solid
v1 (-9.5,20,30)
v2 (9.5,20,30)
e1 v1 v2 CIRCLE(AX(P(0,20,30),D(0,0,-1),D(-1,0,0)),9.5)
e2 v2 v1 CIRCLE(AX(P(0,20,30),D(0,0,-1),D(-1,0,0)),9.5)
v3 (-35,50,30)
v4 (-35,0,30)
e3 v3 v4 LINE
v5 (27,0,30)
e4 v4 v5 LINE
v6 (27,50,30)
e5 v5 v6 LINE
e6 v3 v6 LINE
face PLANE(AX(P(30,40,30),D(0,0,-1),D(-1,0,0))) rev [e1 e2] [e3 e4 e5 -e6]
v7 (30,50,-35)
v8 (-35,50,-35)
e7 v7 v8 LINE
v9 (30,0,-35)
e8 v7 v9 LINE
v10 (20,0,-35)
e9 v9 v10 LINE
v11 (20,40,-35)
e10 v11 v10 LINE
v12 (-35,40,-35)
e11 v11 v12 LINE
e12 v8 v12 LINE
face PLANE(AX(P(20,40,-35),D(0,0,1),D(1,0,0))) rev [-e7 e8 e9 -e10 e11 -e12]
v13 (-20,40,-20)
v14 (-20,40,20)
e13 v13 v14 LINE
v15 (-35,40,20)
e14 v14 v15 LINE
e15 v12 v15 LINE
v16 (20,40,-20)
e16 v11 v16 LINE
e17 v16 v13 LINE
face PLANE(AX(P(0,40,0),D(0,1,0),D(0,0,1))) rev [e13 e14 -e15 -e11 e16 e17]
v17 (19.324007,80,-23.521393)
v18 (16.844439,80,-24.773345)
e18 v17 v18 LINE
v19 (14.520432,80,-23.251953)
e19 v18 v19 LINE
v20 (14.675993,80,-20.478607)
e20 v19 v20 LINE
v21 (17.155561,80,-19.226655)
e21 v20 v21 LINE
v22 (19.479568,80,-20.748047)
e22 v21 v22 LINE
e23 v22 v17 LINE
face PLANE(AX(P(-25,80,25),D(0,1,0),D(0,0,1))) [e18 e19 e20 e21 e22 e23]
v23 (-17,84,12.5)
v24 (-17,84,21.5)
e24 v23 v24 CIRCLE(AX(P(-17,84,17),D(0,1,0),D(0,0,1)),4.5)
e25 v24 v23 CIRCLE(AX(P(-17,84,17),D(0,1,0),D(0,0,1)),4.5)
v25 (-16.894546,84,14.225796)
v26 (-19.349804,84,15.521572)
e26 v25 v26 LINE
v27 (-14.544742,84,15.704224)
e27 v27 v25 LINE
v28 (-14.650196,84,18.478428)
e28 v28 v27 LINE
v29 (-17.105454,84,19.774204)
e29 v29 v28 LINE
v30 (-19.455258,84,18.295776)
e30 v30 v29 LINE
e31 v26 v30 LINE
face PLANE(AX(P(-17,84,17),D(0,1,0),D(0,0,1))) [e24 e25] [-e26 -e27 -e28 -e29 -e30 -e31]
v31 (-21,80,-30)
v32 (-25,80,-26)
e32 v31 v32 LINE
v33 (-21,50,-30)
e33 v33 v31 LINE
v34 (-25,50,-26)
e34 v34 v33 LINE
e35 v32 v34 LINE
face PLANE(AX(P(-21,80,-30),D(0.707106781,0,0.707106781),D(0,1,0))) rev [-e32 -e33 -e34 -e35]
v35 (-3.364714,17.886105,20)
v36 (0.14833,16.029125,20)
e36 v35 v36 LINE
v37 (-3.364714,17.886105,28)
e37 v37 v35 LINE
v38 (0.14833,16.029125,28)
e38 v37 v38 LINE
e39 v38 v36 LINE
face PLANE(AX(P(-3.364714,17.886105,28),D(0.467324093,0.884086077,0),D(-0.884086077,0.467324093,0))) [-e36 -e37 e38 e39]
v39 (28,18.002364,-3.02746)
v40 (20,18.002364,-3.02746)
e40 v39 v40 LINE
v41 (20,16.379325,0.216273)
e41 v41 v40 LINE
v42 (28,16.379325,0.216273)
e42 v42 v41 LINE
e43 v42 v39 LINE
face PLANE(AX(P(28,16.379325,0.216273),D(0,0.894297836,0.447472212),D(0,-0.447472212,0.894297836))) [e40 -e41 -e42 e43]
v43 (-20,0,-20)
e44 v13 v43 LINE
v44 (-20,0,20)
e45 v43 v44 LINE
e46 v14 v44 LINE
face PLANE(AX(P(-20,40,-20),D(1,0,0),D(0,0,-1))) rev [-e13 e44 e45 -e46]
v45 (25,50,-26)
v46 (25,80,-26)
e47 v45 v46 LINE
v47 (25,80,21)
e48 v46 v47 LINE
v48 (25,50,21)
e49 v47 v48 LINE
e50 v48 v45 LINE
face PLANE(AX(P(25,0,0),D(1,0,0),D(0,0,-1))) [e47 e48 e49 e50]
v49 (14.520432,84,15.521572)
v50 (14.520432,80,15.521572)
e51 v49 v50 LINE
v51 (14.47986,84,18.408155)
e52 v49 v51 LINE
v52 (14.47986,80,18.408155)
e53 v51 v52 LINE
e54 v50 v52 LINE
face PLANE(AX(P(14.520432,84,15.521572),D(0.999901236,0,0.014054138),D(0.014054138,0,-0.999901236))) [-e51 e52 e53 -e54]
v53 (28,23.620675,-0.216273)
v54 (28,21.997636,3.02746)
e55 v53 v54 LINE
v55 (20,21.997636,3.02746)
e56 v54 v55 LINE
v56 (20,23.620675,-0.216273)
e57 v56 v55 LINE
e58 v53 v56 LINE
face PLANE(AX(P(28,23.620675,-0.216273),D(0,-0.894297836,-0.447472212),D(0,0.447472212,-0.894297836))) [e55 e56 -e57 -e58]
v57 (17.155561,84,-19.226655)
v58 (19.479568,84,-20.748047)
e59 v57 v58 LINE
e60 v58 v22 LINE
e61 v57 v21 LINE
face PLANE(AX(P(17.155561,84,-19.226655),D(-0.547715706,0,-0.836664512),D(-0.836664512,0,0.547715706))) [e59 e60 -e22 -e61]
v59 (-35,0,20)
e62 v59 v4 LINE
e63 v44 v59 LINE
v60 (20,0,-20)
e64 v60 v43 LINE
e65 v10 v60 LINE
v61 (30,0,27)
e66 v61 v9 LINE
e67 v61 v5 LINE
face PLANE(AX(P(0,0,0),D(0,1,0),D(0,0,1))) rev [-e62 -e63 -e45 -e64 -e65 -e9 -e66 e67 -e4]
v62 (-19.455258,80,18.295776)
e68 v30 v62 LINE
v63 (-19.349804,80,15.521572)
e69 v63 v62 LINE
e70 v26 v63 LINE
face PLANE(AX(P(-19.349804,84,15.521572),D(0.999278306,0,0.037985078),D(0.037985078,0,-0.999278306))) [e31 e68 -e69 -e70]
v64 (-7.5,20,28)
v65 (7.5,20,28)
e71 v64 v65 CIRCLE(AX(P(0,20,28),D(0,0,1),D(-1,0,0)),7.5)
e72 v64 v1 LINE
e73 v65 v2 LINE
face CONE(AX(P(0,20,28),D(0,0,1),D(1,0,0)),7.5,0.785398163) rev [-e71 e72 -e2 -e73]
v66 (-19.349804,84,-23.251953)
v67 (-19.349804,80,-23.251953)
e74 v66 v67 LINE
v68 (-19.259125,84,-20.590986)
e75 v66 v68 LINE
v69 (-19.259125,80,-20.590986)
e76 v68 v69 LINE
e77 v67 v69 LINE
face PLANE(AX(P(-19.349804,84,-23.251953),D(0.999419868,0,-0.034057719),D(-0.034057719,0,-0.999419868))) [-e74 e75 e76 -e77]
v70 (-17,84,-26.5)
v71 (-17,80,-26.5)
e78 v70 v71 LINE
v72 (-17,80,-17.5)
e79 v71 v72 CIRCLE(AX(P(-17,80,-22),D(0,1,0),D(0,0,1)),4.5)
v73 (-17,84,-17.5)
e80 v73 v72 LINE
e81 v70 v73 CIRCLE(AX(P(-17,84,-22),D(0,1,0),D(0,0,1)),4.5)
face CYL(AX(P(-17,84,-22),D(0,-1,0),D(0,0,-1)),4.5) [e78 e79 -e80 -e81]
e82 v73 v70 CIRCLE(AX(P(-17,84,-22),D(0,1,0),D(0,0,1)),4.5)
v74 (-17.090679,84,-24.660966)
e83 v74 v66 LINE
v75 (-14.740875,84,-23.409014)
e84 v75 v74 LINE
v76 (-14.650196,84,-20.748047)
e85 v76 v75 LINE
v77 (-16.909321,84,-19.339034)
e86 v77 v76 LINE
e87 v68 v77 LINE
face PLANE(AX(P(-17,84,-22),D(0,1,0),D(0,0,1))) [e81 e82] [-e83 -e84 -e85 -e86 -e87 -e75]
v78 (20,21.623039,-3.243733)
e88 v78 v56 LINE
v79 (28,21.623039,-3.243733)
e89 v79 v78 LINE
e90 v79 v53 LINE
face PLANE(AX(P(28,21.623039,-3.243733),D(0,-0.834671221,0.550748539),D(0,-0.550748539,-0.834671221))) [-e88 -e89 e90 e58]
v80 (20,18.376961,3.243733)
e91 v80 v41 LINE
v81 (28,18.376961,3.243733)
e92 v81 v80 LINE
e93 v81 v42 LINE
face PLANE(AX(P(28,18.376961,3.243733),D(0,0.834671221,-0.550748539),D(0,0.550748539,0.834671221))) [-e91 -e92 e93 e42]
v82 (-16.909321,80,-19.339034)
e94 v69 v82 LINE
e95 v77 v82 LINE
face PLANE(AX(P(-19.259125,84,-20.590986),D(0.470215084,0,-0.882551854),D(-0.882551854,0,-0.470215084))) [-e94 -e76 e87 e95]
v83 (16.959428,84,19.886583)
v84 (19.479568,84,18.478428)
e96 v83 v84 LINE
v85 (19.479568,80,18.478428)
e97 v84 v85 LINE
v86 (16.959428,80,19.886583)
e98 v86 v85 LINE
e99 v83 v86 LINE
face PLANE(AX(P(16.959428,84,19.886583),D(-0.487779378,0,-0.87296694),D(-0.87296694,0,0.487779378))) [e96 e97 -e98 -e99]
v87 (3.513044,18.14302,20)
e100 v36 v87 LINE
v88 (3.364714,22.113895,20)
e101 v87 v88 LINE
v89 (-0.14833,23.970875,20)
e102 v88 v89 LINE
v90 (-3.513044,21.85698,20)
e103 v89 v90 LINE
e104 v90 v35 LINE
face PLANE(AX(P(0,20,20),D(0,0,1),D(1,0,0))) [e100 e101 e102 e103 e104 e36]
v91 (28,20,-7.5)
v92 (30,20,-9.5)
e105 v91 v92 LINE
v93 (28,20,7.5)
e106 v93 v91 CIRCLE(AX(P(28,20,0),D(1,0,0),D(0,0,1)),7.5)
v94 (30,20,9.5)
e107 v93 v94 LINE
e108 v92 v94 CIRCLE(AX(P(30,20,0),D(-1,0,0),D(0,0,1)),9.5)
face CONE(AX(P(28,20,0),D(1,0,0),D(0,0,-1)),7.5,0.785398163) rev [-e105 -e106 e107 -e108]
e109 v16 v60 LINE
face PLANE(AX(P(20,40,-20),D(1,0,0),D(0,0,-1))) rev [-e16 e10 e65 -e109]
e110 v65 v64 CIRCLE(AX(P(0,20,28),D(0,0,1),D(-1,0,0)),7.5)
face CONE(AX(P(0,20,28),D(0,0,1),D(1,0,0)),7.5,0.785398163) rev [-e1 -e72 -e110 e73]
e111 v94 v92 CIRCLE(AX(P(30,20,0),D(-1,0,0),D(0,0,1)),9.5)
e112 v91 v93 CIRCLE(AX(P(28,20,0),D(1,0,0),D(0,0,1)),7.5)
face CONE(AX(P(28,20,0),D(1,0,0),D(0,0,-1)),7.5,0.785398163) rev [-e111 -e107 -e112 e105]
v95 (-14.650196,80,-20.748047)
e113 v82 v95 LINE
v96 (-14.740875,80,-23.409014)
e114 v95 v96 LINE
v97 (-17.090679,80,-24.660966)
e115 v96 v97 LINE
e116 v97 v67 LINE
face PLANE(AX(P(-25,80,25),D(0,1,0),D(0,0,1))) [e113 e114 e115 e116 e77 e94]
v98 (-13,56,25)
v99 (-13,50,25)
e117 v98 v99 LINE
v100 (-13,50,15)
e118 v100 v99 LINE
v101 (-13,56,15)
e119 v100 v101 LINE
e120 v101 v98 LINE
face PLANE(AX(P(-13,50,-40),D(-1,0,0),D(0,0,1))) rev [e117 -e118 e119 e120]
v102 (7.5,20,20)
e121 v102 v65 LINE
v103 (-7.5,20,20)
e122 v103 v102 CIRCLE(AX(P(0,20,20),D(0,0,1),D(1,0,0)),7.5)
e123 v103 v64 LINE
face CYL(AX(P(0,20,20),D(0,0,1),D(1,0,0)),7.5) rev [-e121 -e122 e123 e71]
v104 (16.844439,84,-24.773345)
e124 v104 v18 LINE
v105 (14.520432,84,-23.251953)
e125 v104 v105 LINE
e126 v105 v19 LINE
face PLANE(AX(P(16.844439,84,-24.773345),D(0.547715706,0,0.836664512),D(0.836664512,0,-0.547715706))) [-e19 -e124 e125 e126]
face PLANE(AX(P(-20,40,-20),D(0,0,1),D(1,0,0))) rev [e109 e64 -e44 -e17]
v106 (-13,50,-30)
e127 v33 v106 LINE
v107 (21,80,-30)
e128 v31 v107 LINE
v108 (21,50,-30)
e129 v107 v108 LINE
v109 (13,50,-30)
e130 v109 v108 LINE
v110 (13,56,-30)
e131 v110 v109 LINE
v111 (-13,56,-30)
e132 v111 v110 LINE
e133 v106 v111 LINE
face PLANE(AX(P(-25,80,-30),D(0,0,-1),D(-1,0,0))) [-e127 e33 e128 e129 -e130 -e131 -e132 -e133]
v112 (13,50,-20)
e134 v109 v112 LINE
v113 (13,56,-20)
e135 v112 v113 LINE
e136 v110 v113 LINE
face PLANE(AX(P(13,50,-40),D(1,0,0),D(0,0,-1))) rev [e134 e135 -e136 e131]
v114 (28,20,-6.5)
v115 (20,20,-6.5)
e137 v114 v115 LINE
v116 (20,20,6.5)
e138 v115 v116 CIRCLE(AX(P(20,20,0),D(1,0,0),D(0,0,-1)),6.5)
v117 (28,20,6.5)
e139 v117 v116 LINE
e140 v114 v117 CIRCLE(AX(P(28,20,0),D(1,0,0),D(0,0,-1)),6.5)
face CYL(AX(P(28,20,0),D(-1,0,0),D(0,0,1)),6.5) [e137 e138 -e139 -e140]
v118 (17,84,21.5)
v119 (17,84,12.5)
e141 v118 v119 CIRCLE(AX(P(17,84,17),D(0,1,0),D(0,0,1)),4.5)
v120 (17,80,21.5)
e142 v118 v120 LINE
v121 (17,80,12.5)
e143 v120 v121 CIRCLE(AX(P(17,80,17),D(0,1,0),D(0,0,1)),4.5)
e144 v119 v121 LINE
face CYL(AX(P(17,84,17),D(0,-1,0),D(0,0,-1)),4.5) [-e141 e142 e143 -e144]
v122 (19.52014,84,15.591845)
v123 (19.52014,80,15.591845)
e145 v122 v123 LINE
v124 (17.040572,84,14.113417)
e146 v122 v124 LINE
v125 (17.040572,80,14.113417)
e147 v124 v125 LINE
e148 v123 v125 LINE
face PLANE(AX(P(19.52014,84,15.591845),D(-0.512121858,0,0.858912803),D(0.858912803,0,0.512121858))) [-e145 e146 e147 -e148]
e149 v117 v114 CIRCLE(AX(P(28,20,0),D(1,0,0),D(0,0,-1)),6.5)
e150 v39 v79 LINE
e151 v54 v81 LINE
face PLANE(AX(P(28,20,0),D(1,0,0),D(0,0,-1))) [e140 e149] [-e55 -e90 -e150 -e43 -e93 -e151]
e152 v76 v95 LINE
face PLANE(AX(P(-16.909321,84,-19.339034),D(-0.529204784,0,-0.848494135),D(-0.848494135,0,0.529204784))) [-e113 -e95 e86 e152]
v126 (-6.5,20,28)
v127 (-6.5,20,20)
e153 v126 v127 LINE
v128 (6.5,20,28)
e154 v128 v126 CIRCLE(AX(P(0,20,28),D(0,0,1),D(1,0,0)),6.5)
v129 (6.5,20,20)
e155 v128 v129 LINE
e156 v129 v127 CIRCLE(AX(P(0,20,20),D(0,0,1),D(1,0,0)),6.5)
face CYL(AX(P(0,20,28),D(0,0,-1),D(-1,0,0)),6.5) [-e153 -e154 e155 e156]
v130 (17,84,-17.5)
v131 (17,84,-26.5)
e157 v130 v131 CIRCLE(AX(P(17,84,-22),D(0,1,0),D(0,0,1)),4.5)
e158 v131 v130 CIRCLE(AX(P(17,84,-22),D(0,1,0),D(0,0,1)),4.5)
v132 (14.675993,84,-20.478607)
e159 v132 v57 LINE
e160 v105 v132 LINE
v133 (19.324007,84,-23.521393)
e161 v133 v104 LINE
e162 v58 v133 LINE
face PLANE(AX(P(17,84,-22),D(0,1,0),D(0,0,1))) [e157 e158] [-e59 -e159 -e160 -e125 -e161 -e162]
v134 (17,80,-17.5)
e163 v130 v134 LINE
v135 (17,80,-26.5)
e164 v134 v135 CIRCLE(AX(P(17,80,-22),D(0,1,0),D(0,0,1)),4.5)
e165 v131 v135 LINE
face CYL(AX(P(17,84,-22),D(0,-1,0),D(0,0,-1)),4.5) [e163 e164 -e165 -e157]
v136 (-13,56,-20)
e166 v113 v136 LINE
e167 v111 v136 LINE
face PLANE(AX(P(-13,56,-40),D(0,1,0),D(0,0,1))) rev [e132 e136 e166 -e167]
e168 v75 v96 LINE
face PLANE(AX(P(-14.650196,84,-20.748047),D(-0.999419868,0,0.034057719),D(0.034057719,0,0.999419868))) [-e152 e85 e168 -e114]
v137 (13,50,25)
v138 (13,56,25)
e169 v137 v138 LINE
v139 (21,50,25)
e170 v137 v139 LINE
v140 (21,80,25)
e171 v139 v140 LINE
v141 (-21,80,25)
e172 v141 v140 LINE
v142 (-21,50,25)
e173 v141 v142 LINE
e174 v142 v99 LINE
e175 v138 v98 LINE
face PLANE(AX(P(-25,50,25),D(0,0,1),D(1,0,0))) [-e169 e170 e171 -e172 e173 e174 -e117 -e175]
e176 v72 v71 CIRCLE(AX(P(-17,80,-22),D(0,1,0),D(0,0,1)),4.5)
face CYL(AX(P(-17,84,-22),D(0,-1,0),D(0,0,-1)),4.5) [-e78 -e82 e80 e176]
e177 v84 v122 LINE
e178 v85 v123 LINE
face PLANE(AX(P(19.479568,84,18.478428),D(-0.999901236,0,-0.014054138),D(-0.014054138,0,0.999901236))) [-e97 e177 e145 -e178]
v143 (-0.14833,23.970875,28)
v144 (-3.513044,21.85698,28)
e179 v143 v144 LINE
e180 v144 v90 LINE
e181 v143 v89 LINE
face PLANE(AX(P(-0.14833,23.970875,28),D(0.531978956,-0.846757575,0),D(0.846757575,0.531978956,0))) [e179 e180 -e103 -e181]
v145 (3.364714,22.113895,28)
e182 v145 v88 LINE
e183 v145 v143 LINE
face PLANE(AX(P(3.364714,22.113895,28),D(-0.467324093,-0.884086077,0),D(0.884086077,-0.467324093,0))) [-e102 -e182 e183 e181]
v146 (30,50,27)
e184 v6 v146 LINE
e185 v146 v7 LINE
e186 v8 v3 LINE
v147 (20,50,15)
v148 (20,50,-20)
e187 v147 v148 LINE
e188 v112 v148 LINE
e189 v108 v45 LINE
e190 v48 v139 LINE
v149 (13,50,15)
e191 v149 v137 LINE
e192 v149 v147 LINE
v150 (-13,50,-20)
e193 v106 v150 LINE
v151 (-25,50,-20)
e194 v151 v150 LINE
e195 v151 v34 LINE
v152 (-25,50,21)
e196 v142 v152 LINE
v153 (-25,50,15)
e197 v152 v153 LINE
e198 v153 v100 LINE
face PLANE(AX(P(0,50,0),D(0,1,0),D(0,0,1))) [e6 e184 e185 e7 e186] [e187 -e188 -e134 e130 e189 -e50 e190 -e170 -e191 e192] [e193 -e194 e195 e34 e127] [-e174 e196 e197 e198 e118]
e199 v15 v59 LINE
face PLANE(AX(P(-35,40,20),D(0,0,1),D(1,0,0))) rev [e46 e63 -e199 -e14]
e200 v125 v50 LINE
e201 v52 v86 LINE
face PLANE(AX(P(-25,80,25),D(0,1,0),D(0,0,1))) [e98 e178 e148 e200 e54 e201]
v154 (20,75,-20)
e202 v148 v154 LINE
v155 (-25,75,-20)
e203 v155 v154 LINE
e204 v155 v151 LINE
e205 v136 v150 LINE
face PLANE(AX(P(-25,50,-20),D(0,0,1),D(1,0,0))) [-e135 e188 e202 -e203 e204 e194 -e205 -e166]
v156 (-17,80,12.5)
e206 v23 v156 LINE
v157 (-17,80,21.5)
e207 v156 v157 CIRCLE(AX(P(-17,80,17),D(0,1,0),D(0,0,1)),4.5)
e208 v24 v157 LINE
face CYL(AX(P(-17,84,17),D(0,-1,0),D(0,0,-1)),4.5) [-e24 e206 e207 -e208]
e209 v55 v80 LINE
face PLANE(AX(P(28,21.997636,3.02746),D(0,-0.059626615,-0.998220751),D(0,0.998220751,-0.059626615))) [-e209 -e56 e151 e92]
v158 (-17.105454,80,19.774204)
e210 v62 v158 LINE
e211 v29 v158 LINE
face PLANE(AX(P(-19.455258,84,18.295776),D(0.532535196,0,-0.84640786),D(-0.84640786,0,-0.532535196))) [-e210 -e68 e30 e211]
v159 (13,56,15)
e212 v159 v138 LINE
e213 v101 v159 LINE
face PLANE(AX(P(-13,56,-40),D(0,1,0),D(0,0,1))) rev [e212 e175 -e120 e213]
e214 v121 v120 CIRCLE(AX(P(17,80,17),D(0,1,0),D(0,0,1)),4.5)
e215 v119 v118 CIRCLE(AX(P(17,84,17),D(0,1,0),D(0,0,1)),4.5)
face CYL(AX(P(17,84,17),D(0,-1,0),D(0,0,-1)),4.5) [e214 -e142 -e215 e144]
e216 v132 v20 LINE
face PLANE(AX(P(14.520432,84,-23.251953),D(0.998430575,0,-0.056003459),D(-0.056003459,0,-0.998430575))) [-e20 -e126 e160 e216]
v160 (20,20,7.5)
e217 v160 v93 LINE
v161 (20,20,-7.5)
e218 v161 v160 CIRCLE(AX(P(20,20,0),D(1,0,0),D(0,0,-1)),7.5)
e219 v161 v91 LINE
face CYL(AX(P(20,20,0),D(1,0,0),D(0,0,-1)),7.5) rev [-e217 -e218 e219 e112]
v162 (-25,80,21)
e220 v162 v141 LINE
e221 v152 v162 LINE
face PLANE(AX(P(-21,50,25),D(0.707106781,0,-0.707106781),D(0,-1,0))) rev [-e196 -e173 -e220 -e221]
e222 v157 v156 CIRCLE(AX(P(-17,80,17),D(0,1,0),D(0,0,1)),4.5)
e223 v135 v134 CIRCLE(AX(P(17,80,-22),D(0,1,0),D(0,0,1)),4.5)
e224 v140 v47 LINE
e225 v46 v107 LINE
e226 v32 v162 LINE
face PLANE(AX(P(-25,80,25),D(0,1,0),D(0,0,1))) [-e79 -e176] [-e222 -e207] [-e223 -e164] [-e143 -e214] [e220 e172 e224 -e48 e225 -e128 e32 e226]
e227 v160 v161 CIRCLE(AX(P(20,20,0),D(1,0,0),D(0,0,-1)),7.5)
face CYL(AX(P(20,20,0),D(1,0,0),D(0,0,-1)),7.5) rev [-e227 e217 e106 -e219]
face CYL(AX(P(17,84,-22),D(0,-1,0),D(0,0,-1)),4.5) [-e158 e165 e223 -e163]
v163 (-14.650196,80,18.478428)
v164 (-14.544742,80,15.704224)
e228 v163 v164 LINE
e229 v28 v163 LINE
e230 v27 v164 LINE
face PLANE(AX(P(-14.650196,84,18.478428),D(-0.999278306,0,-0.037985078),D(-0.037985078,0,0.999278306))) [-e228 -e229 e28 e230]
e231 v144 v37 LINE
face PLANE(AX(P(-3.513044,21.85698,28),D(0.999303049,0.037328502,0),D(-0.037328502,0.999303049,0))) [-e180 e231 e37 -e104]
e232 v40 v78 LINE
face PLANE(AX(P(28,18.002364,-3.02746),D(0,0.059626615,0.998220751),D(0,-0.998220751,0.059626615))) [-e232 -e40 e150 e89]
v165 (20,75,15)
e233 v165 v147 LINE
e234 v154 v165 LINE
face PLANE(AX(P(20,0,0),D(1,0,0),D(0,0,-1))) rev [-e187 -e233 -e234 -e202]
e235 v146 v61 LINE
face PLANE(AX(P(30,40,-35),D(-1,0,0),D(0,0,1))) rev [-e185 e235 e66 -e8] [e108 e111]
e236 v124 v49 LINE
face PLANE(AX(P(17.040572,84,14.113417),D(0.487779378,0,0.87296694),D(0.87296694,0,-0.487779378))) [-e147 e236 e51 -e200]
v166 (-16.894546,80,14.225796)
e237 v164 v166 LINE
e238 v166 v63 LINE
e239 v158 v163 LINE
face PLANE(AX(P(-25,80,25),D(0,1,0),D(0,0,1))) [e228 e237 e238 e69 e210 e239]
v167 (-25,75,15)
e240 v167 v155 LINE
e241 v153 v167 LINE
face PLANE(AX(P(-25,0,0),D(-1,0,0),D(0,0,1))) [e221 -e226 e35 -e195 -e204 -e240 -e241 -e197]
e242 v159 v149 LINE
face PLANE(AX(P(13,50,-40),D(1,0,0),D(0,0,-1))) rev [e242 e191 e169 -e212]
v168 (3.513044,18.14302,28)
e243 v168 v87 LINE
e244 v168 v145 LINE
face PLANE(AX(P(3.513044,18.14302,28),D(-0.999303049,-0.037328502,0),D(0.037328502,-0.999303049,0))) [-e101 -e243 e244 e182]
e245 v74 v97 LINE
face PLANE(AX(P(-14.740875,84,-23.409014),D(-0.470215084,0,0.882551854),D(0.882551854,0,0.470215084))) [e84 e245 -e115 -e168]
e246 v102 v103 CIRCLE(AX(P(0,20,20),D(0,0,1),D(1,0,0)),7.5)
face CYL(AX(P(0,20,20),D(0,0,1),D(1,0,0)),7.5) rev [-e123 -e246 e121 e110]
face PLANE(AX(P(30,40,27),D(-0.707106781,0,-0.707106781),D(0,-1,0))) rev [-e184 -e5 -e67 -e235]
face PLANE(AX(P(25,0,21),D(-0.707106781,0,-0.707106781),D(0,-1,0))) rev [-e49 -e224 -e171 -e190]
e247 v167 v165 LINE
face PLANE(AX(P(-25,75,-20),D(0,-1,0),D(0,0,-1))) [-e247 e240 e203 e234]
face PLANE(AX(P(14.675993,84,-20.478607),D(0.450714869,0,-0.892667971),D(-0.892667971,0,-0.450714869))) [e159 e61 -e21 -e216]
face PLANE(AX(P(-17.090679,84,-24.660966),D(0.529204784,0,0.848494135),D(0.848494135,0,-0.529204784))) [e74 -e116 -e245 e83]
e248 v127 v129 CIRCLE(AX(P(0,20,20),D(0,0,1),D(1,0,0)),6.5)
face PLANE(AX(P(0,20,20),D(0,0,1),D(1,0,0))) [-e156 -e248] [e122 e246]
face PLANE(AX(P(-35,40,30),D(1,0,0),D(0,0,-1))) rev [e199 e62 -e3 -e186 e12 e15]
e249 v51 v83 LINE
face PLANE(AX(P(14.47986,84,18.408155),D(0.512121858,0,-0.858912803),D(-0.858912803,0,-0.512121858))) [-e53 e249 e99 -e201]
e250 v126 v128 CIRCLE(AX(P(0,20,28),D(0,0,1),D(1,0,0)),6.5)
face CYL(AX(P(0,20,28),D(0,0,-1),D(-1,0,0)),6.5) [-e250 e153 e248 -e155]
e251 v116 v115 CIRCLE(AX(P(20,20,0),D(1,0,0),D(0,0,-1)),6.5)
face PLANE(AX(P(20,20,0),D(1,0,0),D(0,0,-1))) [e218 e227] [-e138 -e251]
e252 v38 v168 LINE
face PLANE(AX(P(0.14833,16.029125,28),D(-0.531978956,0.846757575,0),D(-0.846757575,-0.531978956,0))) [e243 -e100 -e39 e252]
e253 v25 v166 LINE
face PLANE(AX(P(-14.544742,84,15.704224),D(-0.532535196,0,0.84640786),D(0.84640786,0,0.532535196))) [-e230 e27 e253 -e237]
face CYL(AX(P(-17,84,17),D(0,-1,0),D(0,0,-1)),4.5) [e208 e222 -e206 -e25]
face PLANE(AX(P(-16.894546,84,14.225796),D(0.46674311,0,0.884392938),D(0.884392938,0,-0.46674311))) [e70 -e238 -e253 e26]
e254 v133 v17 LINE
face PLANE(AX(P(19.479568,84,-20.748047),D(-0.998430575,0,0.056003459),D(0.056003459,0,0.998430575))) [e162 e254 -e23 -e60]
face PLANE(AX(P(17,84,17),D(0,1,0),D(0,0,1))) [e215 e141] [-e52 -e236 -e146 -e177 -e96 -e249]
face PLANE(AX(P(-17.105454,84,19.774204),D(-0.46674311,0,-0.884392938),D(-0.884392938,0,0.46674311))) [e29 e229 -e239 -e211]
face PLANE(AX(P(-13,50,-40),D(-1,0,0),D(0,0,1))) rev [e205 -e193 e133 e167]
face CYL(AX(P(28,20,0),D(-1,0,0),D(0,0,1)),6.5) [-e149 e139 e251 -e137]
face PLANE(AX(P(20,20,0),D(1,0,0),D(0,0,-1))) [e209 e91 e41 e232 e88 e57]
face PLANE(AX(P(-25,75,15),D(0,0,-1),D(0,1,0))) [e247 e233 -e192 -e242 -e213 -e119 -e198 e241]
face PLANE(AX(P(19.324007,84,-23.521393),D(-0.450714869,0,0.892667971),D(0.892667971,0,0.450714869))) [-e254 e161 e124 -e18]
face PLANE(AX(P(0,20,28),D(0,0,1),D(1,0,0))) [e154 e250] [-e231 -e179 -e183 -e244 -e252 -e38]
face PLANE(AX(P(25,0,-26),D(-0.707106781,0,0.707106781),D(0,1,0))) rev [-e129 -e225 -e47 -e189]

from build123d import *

# Parameters (mm, degrees)
BOSS_EXTRUDE1_DEPTH  = 40
SKETCH3_W            = 65
SKETCH3_H            = 65
BOSS_EXTRUDE3_DEPTH  = 10
SKETCH4_R            = 7.5
CUT_EXTRUDE1_DEPTH   = 10
SKETCH5_R            = 7.5
CUT_EXTRUDE2_DEPTH   = 10
SKETCH6_R            = 6.5
BOSS_EXTRUDE4_DEPTH  = 8
SKETCH7_R            = 6.5
BOSS_EXTRUDE5_DEPTH  = 8
CHAMFER1_SIZE        = 2
CHAMFER2_SIZE        = 3
BOSS_EXTRUDE6_DEPTH  = 55
SKETCH10_W           = 55
SKETCH10_H           = 30
CUT_EXTRUDE3_DEPTH   = 5
SKETCH12_W           = 40.885707084
SKETCH12_H           = 30.580268586
BOSS_EXTRUDE10_DEPTH = 5
SKETCH13_W           = 26
SKETCH13_H           = 6
CUT_EXTRUDE4_DEPTH   = 65
SKETCH14_R           = 4.5
BOSS_EXTRUDE11_DEPTH = 4
CHAMFER3_SIZE        = 4


with BuildPart() as part:
    # Sketch1 → Boss-Extrude1 (new body)
    with BuildSketch(Plane(origin=(0, 0, 0), x_dir=(1, 0, 0), z_dir=(0, 1, 0))):
        Polygon((20, 20), (20, 35), (30, 35), (30, -30), (-35, -30), (-35, -20), (-20, -20), (-20, 20), align=None)
    extrude(amount=BOSS_EXTRUDE1_DEPTH)

    # Sketch3 → Boss-Extrude3 (add)
    with BuildSketch(Plane(origin=(0, 40, 0), x_dir=(1, 0, 0), z_dir=(0, 1, 0))):
        with Locations((-2.5, 2.5)):
            Rectangle(SKETCH3_W, SKETCH3_H)
    extrude(amount=BOSS_EXTRUDE3_DEPTH)

    # Sketch4 → Cut-Extrude1 (cut)
    with BuildSketch(Plane.XY.offset(30)):
        with Locations((0, 20)):
            Circle(SKETCH4_R)
    extrude(amount=-CUT_EXTRUDE1_DEPTH, mode=Mode.SUBTRACT)

    # Sketch5 → Cut-Extrude2 (cut)
    with BuildSketch(Plane(origin=(30, 0, 0), x_dir=(0, 0, -1), z_dir=(1, 0, 0))):
        with Locations((0, 20)):
            Circle(SKETCH5_R)
    extrude(amount=-CUT_EXTRUDE2_DEPTH, mode=Mode.SUBTRACT)

    # Sketch6 → Boss-Extrude4 (add)
    with BuildSketch(Plane.XY.offset(20)):
        with Locations((0, 20)):
            Circle(SKETCH6_R)
        Polygon((3.513043884, 18.143020132), (3.364713682, 22.113895314), (-0.148330202, 23.970875182), (-3.513043884, 21.856979868), (-3.364713682, 17.886104686), (0.148330202, 16.029124818), align=None, mode=Mode.SUBTRACT)
    extrude(amount=BOSS_EXTRUDE4_DEPTH)

    # Sketch7 → Boss-Extrude5 (add)
    with BuildSketch(Plane(origin=(20, 0, 0), x_dir=(0, 0, -1), z_dir=(1, 0, 0))):
        with Locations((0, 20)):
            Circle(SKETCH7_R)
        Polygon((3.02745999, 18.002364135), (3.243733401, 21.623039328), (0.216273412, 23.620675193), (-3.02745999, 21.997635865), (-3.243733401, 18.376960672), (-0.216273412, 16.379324807), align=None, mode=Mode.SUBTRACT)
    extrude(amount=BOSS_EXTRUDE5_DEPTH)

    # Chamfer1
    chamfer1_edges = [part.edges().sort_by_distance(p)[0] for p in [
        (-7.5, 20, 30),
        (30, 20, 7.5),
    ]]
    chamfer(chamfer1_edges, length=CHAMFER1_SIZE)

    # Chamfer2
    chamfer2_edges = [part.edges().sort_by_distance(p)[0] for p in [
        (30, 25, 30),
    ]]
    chamfer(chamfer2_edges, length=CHAMFER2_SIZE)

    # Sketch9 → Boss-Extrude6 (add)
    with BuildSketch(Plane(origin=(30, 0, 0), x_dir=(0, 0, -1), z_dir=(1, 0, 0))):
        Polygon((-25, 50), (-25, 80), (30, 80), (30, 50), (20, 50), (20, 75), (-15, 75), (-15, 50), align=None)
    extrude(amount=-BOSS_EXTRUDE6_DEPTH)

    # Sketch10 → Cut-Extrude3 (cut)
    with BuildSketch(Plane(origin=(30, 0, 0), x_dir=(0, 0, -1), z_dir=(1, 0, 0))):
        with Locations((2.5, 65)):
            Rectangle(SKETCH10_W, SKETCH10_H)
    extrude(amount=-CUT_EXTRUDE3_DEPTH, mode=Mode.SUBTRACT)

    # Sketch12 → Boss-Extrude10 (add)
    with BuildSketch(Plane(origin=(25, 0, 0), x_dir=(0, 0, -1), z_dir=(1, 0, 0))):
        with Locations((2.5, 60.722892632)):
            Rectangle(SKETCH12_W, SKETCH12_H)
    extrude(amount=-BOSS_EXTRUDE10_DEPTH)

    # Sketch13 → Cut-Extrude4 (cut)
    with BuildSketch(Plane.XY.offset(25)):
        with Locations((0, 53)):
            Rectangle(SKETCH13_W, SKETCH13_H)
    extrude(amount=-CUT_EXTRUDE4_DEPTH, mode=Mode.SUBTRACT)

    # Sketch14 → Boss-Extrude11 (add)
    # profile 1 of 4: a face of its own
    with BuildSketch(Plane(origin=(0, 80, 0), x_dir=(1, 0, 0), z_dir=(0, 1, 0))):
        with Locations(Location((-17, 22, 0), (0, 0, 270))):
            Circle(SKETCH14_R)
        Polygon((-14.650196001, 20.748047177), (-14.740875051, 23.409013546), (-17.090679051, 24.660966369), (-19.349803999, 23.251952823), (-19.259124949, 20.590986454), (-16.909320949, 19.339033631), align=None, mode=Mode.SUBTRACT)
    # profile 2 of 4: a face of its own
    with BuildSketch(Plane(origin=(0, 80, 0), x_dir=(1, 0, 0), z_dir=(0, 1, 0))):
        with Locations(Location((17, 22, 0), (0, 0, 270))):
            Circle(SKETCH14_R)
        Polygon((19.479568046, 20.748047177), (19.324006972, 23.521392507), (16.844438926, 24.77334533), (14.520431954, 23.251952823), (14.675993028, 20.478607493), (17.155561074, 19.22665467), align=None, mode=Mode.SUBTRACT)
    # profile 3 of 4: a face of its own
    with BuildSketch(Plane(origin=(0, 80, 0), x_dir=(1, 0, 0), z_dir=(0, 1, 0))):
        with Locations(Location((17, -17, 0), (0, 0, 270))):
            Circle(SKETCH14_R)
        Polygon((19.479568046, -18.478428301), (19.520140489, -15.591845232), (17.040572443, -14.113416931), (14.520431954, -15.521571699), (14.479859511, -18.408154768), (16.959427557, -19.886583069), align=None, mode=Mode.SUBTRACT)
    # profile 4 of 4: a face of its own
    with BuildSketch(Plane(origin=(0, 80, 0), x_dir=(1, 0, 0), z_dir=(0, 1, 0))):
        with Locations(Location((-17, -17, 0), (0, 0, 270))):
            Circle(SKETCH14_R)
        Polygon((-14.650196001, -18.478428301), (-14.544741534, -15.704224193), (-16.894545533, -14.225795892), (-19.349803999, -15.521571699), (-19.455258466, -18.295775807), (-17.105454467, -19.774204108), align=None, mode=Mode.SUBTRACT)
    extrude(amount=BOSS_EXTRUDE11_DEPTH)

    # Chamfer3
    chamfer3_edges = [part.edges().sort_by_distance(p)[0] for p in [
        (-25, 65, 25),
        (-25, 65, -30),
        (25, 65, 25),
        (25, 65, -30),
    ]]
    chamfer(chamfer3_edges, length=CHAMFER3_SIZE)


solid = part.part
